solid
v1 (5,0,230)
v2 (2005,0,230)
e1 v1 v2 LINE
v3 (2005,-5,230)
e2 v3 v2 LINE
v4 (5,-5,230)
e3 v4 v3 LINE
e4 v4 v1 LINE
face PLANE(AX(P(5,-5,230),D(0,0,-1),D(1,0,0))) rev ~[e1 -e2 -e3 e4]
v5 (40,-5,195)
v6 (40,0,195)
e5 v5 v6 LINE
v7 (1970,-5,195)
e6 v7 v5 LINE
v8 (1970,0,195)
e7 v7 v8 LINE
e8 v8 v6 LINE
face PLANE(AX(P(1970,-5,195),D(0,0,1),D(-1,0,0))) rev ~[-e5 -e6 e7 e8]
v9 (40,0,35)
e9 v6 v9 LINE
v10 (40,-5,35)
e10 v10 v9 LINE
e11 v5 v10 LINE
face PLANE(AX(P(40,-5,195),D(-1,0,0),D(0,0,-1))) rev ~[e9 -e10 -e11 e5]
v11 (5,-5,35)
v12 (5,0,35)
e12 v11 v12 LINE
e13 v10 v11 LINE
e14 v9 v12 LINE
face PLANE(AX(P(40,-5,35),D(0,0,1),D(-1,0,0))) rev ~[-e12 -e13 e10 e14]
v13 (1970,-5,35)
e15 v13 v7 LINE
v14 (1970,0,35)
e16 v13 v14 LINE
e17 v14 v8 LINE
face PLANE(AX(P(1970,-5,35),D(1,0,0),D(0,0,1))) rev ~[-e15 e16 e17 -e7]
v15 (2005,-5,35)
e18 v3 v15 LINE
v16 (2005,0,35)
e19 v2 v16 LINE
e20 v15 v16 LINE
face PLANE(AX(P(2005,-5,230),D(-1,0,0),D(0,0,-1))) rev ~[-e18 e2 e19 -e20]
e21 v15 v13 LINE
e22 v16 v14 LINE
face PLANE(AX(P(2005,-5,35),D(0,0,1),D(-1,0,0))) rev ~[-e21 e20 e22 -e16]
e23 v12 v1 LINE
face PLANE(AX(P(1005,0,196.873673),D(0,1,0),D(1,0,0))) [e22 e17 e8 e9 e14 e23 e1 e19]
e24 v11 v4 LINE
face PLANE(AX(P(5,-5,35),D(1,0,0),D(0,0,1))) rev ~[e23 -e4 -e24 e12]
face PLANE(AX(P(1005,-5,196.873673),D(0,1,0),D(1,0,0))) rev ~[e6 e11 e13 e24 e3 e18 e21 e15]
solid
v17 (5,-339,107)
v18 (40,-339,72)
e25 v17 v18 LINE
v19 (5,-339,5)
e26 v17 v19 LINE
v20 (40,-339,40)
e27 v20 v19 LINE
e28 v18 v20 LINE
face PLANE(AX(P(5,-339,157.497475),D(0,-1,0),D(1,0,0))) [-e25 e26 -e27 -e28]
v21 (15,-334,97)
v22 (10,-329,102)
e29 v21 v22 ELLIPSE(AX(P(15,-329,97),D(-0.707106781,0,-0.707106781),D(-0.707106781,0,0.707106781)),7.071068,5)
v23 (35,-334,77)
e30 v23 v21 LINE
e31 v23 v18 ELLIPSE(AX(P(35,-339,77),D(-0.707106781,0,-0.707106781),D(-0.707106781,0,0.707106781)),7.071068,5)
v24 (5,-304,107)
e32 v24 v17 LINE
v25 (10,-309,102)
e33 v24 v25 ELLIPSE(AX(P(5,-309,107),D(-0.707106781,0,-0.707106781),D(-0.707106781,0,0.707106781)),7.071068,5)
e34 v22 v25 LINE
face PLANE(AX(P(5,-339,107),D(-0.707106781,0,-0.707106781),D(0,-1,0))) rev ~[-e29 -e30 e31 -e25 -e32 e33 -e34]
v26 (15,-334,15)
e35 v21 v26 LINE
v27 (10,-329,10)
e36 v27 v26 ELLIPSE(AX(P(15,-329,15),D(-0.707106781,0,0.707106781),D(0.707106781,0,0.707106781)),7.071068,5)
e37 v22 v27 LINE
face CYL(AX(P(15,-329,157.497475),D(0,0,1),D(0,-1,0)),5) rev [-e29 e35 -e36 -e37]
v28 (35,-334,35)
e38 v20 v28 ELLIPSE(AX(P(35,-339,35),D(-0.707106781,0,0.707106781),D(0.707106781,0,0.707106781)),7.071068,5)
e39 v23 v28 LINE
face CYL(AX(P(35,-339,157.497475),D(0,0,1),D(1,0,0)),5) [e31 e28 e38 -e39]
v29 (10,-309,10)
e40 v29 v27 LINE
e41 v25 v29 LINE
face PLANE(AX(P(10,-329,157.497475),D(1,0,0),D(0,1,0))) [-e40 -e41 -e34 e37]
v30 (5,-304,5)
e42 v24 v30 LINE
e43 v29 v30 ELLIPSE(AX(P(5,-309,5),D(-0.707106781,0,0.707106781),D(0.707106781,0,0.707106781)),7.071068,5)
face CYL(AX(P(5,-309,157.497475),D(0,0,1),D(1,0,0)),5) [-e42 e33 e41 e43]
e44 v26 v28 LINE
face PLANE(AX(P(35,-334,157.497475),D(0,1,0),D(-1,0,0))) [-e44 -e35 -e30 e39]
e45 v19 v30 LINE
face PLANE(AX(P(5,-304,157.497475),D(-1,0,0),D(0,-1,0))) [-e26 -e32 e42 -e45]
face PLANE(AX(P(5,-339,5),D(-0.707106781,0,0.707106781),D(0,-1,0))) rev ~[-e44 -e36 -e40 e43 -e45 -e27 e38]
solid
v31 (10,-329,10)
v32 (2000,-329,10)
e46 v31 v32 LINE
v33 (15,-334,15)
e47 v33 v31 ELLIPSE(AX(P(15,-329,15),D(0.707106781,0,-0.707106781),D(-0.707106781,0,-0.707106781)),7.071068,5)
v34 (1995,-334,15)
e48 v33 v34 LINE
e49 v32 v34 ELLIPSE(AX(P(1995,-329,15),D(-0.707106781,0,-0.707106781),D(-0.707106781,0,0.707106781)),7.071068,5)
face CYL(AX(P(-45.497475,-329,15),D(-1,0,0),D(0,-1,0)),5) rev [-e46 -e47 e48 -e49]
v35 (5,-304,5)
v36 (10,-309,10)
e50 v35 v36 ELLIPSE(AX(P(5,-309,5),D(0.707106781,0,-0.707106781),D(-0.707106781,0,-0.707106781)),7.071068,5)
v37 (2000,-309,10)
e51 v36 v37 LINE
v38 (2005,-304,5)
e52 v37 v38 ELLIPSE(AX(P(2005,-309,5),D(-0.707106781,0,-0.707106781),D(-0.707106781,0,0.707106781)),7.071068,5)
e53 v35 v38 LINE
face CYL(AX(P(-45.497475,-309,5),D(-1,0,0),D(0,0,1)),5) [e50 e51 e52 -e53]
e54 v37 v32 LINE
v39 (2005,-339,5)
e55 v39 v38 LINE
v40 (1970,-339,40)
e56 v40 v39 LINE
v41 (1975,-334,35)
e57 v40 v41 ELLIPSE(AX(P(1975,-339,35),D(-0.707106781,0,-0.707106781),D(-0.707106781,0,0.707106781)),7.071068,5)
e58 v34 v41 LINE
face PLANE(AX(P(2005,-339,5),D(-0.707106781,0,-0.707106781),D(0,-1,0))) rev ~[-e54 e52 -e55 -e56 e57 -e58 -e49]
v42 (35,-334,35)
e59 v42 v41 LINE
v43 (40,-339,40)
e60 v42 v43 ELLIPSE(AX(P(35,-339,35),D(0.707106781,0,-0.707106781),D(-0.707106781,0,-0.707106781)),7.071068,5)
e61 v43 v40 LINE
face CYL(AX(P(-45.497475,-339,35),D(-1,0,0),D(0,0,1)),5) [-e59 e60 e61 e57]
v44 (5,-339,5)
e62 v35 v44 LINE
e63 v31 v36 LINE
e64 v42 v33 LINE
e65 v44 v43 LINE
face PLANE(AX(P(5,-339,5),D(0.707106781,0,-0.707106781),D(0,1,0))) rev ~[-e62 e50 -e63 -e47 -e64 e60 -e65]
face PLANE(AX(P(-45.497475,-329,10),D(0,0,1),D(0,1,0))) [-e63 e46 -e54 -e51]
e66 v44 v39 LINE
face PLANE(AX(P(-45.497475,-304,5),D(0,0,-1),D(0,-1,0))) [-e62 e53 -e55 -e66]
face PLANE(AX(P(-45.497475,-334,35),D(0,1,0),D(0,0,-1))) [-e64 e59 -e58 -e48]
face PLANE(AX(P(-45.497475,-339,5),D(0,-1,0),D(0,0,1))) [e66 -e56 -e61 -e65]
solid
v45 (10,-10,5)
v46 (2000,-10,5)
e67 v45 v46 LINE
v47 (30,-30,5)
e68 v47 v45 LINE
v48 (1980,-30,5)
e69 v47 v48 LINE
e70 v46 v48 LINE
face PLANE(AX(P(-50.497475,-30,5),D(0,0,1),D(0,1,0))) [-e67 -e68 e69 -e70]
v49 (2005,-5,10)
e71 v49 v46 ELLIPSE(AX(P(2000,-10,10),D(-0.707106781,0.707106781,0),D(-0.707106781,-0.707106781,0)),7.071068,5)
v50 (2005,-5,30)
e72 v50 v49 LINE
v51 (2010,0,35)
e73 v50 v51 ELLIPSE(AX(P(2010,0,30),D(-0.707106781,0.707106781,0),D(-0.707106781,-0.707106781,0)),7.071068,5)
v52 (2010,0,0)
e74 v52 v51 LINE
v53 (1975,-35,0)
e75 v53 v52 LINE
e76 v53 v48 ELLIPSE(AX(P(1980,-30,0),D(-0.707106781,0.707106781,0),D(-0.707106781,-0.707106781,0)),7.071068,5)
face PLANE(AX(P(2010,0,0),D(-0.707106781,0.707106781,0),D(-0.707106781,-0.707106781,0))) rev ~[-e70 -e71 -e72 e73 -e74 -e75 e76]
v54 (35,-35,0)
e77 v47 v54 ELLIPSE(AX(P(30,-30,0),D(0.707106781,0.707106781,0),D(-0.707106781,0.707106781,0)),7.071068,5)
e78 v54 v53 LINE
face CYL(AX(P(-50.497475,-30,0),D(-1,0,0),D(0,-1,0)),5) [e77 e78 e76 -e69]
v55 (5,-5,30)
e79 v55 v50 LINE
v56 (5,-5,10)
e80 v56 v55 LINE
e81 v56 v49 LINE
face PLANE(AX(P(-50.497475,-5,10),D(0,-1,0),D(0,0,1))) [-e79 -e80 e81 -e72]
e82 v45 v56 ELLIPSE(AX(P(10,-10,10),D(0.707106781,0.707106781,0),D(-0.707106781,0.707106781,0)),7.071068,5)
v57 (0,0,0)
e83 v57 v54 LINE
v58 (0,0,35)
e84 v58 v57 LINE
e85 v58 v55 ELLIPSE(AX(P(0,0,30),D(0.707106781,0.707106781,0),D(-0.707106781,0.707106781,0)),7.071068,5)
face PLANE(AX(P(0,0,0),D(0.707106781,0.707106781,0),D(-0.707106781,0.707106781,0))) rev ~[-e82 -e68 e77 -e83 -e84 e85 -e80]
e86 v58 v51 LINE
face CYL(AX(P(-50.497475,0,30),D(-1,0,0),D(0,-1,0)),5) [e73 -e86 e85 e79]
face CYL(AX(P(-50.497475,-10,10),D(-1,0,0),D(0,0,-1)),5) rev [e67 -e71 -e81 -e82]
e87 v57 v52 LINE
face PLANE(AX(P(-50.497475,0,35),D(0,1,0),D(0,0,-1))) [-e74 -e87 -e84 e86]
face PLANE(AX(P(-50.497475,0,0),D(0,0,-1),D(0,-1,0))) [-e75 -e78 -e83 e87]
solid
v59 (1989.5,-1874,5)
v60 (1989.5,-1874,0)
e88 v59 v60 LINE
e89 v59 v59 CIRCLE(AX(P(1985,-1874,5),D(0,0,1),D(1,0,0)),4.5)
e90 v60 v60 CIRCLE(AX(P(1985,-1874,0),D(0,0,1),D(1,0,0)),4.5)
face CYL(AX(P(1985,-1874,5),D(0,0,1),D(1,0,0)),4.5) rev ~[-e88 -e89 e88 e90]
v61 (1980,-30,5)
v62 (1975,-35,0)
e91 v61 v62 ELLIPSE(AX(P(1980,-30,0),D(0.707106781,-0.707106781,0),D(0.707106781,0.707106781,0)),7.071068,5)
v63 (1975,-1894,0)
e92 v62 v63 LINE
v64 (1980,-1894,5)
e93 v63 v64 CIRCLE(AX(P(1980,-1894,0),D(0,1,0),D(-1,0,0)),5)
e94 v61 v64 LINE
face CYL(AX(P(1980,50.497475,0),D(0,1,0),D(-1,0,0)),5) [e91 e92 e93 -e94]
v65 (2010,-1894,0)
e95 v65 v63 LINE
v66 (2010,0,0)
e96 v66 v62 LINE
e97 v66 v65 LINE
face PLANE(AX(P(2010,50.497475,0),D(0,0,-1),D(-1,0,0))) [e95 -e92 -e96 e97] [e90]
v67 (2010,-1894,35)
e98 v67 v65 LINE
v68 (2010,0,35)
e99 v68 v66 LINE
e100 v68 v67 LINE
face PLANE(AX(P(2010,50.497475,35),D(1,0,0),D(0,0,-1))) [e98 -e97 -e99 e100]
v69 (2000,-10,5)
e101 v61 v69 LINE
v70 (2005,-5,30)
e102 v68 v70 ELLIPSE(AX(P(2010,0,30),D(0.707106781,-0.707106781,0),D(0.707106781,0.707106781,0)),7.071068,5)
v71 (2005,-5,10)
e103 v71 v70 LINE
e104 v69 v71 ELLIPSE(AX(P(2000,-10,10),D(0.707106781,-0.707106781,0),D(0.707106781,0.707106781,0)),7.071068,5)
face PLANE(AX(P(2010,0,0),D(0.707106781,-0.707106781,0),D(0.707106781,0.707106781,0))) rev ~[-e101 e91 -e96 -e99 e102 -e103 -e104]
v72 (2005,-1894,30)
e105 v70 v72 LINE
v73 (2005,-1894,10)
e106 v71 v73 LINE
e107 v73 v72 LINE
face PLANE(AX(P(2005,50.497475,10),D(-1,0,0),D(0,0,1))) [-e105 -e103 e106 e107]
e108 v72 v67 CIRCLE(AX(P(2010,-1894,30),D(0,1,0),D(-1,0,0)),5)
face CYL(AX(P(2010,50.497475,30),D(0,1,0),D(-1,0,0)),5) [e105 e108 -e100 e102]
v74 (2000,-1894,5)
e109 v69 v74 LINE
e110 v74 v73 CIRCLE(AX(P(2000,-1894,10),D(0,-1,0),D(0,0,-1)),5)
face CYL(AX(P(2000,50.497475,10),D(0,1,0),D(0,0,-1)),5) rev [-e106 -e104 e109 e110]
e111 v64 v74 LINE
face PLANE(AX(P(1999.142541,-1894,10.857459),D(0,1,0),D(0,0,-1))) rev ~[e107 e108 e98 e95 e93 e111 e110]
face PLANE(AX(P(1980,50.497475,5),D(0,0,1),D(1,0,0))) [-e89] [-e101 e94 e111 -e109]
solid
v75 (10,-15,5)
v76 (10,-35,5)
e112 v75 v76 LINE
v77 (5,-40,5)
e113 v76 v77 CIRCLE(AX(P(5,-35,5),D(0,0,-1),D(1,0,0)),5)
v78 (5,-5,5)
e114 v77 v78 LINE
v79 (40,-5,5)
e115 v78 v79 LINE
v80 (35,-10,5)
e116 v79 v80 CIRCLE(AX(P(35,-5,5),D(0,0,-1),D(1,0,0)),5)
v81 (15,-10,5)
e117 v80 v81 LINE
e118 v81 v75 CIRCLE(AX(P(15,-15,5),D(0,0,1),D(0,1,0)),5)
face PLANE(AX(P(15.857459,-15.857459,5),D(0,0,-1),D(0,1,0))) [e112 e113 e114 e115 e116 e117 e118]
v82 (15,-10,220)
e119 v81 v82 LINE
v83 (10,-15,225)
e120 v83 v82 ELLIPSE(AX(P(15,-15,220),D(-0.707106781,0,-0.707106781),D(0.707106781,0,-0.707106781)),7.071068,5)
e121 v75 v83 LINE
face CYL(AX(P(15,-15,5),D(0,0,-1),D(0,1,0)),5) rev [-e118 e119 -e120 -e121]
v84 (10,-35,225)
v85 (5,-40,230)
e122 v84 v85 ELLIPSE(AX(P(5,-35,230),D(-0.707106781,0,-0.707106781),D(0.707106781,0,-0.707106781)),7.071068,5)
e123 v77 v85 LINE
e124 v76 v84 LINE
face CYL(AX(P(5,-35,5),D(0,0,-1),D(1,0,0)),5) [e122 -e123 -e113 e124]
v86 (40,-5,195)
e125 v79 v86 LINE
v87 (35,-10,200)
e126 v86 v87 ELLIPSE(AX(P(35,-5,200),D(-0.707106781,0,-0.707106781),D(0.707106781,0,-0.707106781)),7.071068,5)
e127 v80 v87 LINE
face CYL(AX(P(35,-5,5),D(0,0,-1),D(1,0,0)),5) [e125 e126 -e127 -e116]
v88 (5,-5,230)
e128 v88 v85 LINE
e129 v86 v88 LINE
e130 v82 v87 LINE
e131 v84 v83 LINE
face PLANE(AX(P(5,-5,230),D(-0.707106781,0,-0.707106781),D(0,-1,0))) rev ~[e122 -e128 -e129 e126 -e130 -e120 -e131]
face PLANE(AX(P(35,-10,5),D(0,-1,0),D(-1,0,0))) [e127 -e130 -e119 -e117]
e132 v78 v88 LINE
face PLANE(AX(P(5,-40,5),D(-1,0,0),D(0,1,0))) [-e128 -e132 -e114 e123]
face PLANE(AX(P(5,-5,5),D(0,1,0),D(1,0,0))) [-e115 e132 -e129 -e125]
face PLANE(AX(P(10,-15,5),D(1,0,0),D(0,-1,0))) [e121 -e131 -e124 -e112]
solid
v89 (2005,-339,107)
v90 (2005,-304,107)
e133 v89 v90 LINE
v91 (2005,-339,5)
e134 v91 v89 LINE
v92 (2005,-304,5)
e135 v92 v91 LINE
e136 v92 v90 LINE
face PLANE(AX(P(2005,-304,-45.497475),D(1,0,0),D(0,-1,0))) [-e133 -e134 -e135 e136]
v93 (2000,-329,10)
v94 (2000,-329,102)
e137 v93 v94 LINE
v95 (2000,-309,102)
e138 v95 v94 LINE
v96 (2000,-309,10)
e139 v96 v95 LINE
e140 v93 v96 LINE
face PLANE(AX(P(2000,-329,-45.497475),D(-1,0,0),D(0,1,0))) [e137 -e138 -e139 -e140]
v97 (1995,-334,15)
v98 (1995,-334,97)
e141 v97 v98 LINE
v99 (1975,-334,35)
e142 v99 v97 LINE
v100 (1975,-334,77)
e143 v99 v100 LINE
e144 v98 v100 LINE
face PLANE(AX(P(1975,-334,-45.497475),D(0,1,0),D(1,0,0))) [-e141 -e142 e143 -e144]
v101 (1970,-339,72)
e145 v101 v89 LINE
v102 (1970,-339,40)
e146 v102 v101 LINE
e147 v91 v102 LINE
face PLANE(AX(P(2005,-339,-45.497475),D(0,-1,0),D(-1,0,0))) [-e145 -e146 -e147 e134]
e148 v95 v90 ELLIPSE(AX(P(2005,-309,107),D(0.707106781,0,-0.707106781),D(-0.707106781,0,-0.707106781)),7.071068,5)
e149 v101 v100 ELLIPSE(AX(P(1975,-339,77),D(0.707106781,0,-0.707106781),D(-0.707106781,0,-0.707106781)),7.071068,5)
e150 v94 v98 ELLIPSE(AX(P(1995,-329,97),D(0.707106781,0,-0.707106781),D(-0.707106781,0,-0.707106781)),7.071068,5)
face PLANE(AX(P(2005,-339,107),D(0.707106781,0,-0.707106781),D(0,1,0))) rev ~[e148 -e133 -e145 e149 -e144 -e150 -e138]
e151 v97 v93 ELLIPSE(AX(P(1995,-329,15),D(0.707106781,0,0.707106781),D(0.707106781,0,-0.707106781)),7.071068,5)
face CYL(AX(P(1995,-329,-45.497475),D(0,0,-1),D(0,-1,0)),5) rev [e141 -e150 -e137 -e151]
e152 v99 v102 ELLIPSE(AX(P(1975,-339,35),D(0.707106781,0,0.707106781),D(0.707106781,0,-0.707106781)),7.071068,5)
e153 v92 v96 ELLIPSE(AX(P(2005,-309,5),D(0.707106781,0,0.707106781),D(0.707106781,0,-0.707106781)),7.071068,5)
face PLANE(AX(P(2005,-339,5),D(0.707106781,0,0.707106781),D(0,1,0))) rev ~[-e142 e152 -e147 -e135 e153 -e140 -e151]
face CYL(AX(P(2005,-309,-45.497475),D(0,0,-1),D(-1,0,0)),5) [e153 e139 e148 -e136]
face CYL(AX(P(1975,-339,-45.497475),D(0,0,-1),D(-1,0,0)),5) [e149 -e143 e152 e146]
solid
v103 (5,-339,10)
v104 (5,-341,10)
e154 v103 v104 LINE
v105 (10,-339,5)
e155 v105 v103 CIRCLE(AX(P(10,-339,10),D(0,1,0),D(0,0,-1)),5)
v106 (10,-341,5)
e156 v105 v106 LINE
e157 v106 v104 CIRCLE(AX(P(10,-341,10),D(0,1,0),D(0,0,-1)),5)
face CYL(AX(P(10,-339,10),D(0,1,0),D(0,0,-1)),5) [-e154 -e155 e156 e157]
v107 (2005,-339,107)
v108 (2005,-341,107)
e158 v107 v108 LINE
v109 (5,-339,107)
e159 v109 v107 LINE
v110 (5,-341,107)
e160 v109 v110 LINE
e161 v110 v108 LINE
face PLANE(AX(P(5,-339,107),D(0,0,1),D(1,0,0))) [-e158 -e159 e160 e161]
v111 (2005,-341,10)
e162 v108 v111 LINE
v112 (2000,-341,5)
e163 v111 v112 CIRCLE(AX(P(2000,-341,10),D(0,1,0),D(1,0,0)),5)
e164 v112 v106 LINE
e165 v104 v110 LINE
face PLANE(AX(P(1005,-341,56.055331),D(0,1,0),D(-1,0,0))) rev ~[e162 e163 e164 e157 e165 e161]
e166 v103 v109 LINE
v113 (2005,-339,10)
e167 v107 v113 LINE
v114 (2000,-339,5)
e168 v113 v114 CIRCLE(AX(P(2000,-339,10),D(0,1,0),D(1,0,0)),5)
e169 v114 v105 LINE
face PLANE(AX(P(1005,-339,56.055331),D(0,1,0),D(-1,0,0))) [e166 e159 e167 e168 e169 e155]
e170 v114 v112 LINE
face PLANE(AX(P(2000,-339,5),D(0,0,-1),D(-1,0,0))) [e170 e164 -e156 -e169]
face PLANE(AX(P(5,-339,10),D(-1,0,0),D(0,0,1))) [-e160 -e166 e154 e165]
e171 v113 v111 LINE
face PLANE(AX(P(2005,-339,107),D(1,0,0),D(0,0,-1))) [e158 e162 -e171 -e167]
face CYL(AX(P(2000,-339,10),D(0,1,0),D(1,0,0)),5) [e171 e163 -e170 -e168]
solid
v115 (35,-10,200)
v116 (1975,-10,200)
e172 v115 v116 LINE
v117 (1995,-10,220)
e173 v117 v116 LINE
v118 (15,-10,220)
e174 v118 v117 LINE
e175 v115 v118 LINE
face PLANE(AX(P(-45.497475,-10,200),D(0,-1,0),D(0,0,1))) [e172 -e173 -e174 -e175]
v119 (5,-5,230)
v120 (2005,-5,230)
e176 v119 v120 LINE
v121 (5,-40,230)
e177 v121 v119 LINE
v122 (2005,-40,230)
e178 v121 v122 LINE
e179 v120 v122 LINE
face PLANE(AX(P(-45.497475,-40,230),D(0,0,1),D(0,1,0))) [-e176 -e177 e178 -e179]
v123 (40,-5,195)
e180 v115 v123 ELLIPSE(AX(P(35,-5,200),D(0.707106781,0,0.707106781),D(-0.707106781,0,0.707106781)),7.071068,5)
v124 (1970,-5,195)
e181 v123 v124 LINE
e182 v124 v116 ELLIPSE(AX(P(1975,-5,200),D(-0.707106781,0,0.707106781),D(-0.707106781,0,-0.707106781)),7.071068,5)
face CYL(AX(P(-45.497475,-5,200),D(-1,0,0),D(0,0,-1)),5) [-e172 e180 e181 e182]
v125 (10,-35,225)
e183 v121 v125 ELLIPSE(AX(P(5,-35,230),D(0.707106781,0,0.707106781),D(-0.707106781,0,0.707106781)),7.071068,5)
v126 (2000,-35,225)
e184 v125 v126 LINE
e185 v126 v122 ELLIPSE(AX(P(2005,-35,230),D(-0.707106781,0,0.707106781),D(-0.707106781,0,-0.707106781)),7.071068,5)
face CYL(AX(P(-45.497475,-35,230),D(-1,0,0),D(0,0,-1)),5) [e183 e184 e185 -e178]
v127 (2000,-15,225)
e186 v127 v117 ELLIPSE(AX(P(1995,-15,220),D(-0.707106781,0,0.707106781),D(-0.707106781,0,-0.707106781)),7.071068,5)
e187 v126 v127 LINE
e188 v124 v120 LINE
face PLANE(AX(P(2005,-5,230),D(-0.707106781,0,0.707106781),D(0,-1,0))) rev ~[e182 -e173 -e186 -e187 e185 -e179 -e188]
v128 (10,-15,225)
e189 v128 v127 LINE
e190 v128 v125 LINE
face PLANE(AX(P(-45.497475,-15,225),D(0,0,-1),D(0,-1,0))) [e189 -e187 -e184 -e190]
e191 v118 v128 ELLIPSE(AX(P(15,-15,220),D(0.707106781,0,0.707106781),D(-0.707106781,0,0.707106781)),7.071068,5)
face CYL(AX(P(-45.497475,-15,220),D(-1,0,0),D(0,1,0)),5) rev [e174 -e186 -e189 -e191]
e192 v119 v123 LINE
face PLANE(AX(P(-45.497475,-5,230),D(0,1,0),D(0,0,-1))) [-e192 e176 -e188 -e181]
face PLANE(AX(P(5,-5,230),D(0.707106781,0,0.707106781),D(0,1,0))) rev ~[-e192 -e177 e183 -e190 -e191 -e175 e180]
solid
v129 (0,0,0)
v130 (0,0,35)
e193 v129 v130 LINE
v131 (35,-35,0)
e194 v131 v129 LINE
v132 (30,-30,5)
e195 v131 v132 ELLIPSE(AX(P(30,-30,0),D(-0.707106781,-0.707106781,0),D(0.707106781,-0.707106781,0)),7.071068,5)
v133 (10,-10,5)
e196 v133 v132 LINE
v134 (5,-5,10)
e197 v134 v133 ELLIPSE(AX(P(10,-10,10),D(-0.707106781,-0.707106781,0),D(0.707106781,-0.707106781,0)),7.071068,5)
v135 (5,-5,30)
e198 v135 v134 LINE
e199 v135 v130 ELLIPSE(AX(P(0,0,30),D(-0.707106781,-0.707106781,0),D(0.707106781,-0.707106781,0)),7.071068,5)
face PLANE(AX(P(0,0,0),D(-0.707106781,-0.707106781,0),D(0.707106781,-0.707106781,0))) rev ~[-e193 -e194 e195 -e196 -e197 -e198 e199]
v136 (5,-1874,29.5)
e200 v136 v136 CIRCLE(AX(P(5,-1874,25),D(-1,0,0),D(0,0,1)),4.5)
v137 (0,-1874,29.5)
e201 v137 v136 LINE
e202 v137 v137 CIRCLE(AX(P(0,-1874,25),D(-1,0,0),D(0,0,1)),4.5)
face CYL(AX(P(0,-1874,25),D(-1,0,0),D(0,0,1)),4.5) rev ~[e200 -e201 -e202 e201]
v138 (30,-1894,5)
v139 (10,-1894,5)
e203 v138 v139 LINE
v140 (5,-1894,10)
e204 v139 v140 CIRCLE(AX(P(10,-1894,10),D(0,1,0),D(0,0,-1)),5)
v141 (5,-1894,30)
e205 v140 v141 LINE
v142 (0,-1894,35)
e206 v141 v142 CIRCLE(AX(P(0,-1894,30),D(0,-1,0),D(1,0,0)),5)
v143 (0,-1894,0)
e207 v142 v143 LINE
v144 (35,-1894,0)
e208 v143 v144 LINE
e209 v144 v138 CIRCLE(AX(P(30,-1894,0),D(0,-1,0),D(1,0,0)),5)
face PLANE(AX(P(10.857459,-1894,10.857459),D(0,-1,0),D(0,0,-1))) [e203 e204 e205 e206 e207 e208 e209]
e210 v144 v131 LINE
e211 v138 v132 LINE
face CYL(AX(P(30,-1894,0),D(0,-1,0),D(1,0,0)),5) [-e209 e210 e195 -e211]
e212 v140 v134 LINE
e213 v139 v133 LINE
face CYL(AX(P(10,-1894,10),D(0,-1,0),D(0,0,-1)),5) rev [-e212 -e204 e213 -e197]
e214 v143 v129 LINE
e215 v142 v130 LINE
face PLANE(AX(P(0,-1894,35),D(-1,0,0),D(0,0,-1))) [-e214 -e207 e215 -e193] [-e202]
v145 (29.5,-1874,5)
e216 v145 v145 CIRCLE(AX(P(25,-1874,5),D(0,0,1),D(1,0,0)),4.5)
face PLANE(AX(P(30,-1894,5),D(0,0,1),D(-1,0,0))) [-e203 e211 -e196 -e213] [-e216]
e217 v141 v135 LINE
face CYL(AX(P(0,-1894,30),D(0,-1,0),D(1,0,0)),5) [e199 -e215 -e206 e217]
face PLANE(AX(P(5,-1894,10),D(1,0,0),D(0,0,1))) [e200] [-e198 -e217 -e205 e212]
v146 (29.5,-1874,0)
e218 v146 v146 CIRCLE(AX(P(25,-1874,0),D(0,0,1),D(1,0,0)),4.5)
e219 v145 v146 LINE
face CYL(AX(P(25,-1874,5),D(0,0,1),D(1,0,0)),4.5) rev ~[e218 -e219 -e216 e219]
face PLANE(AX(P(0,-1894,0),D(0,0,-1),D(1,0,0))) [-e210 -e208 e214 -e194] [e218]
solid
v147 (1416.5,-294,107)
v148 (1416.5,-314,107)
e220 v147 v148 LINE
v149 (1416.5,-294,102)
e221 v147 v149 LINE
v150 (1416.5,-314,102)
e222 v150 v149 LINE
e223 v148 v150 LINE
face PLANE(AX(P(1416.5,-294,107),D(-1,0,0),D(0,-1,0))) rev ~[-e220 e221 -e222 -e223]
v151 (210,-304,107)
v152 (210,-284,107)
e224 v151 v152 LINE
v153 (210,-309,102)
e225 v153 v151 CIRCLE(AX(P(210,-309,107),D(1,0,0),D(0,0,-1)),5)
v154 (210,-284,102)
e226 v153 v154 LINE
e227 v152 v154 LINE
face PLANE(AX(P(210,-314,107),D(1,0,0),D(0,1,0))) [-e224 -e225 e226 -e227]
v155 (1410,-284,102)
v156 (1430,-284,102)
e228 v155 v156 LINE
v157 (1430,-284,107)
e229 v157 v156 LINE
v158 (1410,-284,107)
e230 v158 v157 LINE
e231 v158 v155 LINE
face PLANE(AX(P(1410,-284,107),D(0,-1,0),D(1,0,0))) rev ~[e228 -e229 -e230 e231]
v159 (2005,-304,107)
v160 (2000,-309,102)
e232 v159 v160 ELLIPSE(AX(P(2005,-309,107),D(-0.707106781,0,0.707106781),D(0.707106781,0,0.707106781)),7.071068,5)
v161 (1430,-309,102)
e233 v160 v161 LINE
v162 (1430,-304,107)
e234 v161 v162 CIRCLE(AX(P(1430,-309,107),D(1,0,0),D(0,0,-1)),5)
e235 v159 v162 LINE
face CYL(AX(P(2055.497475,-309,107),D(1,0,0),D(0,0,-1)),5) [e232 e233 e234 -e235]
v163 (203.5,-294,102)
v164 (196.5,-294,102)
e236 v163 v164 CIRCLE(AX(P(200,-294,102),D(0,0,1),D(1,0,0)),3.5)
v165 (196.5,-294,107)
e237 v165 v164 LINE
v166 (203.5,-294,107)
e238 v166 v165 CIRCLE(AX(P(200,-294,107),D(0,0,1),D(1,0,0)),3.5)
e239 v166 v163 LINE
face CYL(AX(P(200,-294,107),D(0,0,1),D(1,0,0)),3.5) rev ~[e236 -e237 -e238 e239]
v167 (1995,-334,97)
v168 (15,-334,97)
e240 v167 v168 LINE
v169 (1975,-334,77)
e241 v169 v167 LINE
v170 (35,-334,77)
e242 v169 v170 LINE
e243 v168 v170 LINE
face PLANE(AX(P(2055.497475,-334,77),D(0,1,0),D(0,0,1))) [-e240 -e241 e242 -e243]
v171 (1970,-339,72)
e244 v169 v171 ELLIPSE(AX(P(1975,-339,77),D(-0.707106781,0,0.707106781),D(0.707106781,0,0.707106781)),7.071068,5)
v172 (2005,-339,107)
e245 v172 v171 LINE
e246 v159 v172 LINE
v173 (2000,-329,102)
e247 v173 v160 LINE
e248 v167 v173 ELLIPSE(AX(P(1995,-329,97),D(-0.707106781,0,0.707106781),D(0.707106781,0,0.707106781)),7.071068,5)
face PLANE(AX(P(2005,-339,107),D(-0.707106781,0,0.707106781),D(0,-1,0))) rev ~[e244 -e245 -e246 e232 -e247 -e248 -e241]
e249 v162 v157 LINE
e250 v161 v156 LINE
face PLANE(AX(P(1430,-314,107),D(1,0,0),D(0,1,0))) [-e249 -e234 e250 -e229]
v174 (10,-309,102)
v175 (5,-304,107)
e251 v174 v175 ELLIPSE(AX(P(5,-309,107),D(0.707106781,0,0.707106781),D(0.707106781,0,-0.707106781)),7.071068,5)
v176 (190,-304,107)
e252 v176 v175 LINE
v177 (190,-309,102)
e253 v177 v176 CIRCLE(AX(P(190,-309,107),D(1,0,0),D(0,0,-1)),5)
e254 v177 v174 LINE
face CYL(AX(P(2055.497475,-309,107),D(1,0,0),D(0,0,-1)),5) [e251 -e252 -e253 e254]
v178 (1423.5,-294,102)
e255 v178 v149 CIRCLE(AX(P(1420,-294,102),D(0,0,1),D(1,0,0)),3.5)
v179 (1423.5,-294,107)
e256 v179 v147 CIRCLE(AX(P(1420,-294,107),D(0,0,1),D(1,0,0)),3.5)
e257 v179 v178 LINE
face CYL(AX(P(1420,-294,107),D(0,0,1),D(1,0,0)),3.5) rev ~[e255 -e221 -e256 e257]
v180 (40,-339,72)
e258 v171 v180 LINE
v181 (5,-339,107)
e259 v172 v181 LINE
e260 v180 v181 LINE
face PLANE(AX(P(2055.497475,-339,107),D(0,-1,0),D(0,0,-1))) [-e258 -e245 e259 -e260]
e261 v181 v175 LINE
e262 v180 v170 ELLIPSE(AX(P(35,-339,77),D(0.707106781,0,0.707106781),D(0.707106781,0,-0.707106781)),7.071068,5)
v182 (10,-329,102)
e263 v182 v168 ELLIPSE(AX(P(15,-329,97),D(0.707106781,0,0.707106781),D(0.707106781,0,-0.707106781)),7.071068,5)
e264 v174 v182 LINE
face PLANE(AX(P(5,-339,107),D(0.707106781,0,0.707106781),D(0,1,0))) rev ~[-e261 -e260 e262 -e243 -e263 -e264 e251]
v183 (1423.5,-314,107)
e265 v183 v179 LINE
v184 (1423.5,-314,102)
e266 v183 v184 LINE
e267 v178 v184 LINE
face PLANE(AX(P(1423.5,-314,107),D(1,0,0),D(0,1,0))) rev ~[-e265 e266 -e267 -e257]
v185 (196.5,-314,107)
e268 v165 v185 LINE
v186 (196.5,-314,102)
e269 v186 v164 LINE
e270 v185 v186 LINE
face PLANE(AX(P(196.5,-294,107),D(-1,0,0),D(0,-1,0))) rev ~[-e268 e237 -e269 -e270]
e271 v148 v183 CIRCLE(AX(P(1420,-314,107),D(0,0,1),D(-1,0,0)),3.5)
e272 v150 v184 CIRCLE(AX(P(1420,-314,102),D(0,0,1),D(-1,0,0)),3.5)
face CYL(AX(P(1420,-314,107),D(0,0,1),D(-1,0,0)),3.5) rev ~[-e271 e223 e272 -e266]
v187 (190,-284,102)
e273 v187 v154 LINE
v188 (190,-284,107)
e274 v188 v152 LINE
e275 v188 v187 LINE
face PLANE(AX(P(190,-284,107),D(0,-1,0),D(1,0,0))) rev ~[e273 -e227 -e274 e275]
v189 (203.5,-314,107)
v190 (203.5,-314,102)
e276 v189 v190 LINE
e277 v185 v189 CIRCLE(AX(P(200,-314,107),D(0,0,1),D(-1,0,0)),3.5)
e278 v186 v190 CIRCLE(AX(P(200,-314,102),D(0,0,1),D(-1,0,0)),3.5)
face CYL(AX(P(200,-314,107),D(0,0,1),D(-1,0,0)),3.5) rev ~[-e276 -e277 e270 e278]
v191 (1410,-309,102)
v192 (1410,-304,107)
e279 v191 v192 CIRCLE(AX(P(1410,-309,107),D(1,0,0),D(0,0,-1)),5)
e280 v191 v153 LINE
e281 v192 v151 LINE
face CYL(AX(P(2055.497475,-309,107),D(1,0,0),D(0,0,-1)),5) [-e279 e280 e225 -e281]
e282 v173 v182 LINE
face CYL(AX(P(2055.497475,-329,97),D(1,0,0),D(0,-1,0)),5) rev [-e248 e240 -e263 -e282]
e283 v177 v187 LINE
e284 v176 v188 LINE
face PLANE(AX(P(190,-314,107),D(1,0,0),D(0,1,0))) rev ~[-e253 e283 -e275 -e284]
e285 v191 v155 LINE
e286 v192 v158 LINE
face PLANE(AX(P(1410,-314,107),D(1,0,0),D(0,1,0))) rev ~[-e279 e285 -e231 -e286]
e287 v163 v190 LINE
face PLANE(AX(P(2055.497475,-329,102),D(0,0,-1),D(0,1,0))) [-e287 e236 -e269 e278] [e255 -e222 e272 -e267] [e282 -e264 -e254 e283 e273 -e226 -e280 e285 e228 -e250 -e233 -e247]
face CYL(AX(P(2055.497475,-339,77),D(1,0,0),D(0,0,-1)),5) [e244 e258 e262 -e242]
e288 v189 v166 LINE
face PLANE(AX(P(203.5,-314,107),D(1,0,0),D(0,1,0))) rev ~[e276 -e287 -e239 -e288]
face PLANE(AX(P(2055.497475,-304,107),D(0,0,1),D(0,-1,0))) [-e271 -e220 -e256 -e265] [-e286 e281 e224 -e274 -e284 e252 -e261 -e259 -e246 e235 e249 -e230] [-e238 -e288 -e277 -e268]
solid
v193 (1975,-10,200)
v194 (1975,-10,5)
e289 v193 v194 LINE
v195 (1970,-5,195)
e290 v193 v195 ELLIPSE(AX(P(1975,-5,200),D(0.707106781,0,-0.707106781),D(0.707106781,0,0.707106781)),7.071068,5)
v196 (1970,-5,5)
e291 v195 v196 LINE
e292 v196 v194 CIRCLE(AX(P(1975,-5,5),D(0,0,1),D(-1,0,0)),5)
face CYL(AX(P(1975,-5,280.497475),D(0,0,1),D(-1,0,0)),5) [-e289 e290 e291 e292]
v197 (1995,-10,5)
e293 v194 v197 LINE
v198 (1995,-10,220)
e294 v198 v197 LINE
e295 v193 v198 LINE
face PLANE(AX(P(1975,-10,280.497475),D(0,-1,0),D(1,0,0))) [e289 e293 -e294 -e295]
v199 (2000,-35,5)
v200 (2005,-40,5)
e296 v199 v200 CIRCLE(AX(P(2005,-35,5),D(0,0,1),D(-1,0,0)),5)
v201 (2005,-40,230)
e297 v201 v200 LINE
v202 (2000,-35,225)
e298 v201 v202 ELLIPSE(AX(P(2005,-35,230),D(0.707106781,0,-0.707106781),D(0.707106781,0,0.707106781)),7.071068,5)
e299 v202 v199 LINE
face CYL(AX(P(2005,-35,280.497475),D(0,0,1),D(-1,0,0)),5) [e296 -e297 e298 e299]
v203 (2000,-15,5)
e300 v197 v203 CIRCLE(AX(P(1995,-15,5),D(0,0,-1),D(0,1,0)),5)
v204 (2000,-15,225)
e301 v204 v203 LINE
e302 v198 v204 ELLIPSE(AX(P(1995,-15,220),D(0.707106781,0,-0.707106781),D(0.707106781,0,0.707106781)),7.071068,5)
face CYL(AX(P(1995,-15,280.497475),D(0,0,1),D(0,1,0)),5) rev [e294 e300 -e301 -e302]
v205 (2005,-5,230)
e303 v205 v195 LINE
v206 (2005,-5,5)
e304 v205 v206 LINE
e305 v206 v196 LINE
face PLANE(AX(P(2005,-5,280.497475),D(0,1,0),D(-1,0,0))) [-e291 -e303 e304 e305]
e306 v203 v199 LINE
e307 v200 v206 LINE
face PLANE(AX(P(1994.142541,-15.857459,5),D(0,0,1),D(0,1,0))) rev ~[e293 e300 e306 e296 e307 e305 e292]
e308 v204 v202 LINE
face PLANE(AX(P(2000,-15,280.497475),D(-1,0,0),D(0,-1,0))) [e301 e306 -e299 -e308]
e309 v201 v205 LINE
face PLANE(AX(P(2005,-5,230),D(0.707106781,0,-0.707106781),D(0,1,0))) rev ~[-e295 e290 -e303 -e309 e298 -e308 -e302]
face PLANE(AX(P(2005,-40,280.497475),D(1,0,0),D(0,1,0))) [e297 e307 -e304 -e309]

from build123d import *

# Parameters (mm, degrees)
MEMBER_1_DEPTH        = 1944.497474683
MEMBER_1_2_DEPTH      = 2060.497474683
MEMBER_1_2_DEPTH_BACK = 50.497474683
MEMBER_1_3_DEPTH      = 1944.497474683
MEMBER_2_DEPTH        = 275.497474683
MEMBER_2_2_DEPTH      = 2100.994949366
MEMBER_2_3_DEPTH      = 275.497474683
MEMBER_3_DEPTH        = 152.497474683
MEMBER_3_DEPTH_BACK   = 50.497474683
MEMBER_3_2_DEPTH      = 2100.994949366
MEMBER_3_3_DEPTH      = 202.994949366
MEMBER_3_4_DEPTH      = 2100.994949366
SKETCH_8_R            = 4.5
CUT_EXTRUDE_1_DEPTH   = 10
SKETCH_9_R            = 4.5
CUT_EXTRUDE_2_DEPTH   = 697
EXTRUDE_1_DEPTH       = 5
EXTRUDE_2_DEPTH       = 2
SKETCH_13_W           = 20
SKETCH_13_H           = 30
EXTRUDE_3_DEPTH       = 5
CUT_EXTRUDE_3_DEPTH   = 10


with BuildPart() as part:
    # Sketch1 on segment 1 (carried to segment 1) → Member 1 (new body)
    with BuildSketch(Plane.ZX.offset(-1894)):
        with BuildLine():
            Line((0, 0), (0, 35))
            ThreePointArc((0, 35), (3.535533906, 33.535533906), (5, 30))
            Line((5, 30), (5, 10))
            ThreePointArc((5, 10), (6.464466094, 6.464466094), (10, 5))
            Line((10, 5), (30, 5))
            ThreePointArc((30, 5), (33.535533906, 3.535533906), (35, 0))
            Line((35, 0), (0, 0))
        make_face()
    extrude(amount=MEMBER_1_DEPTH)

    # Member 1 mitre 1
    split(bisect_by=Plane(origin=(0, 0, 0), x_dir=(0.707106781, -0.707106781, 0), z_dir=(-0.707106781, -0.707106781, 0)), keep=Keep.TOP)


with BuildPart() as body_2:
    # Sketch1 → Member 1 2 (new, two sides: drawn at the far end of the back side and taken through both)
    with BuildSketch(Plane(origin=(0, 0, 0), x_dir=(0, 0, 1), z_dir=(1, 0, 0)).offset(-MEMBER_1_2_DEPTH_BACK)):
        with BuildLine():
            Line((0, 0), (0, 35))
            ThreePointArc((0, 35), (3.535533906, 33.535533906), (5, 30))
            Line((5, 30), (5, 10))
            ThreePointArc((5, 10), (6.464466094, 6.464466094), (10, 5))
            Line((10, 5), (30, 5))
            ThreePointArc((30, 5), (33.535533906, 3.535533906), (35, 0))
            Line((35, 0), (0, 0))
        make_face()
    extrude(amount=MEMBER_1_2_DEPTH + MEMBER_1_2_DEPTH_BACK)

    # Member 1 2 mitre 1
    split(bisect_by=Plane(origin=(0, 0, 0), x_dir=(-0.707106781, 0.707106781, 0), z_dir=(0.707106781, 0.707106781, 0)), keep=Keep.TOP)

    # Member 1 2 mitre 2
    split(bisect_by=Plane(origin=(2010, 0, 0), x_dir=(-0.707106781, -0.707106781, 0), z_dir=(-0.707106781, 0.707106781, 0)), keep=Keep.TOP)


with BuildPart() as body_3:
    # Sketch1 on segment 3 (carried to segment 3) → Member 1 3 (new body)
    with BuildSketch(Plane(origin=(2010, 50.497474683, 0), x_dir=(0, 0, 1), z_dir=(0, -1, 0))):
        with BuildLine():
            Line((0, 0), (0, 35))
            ThreePointArc((0, 35), (3.535533906, 33.535533906), (5, 30))
            Line((5, 30), (5, 10))
            ThreePointArc((5, 10), (6.464466094, 6.464466094), (10, 5))
            Line((10, 5), (30, 5))
            ThreePointArc((30, 5), (33.535533906, 3.535533906), (35, 0))
            Line((35, 0), (0, 0))
        make_face()
    extrude(amount=MEMBER_1_3_DEPTH)

    # Member 1 3 mitre 1
    split(bisect_by=Plane(origin=(2010, 0, 0), x_dir=(0.707106781, 0.707106781, 0), z_dir=(0.707106781, -0.707106781, 0)), keep=Keep.TOP)


with BuildPart() as body_4:
    # Sketch11 → Member 2 (new body)
    with BuildSketch(Plane(origin=(5, -5, 5), x_dir=(0, -1, 0), z_dir=(0, 0, 1))):
        with BuildLine():
            Line((0, 0), (0, 35))
            ThreePointArc((0, 35), (3.535533906, 33.535533906), (5, 30))
            Line((5, 30), (5, 10))
            ThreePointArc((5, 10), (6.464466094, 6.464466094), (10, 5))
            Line((10, 5), (30, 5))
            ThreePointArc((30, 5), (33.535533906, 3.535533906), (35, 0))
            Line((35, 0), (0, 0))
        make_face()
    extrude(amount=MEMBER_2_DEPTH)

    # Member 2 mitre 1
    split(bisect_by=Plane(origin=(5, -5, 230), x_dir=(0, -1, 0), z_dir=(-0.707106781, 0, -0.707106781)), keep=Keep.TOP)


with BuildPart() as body_5:
    # Sketch11 on segment 2 (carried to segment 2) → Member 2 2 (new body)
    with BuildSketch(Plane(origin=(-45.497474683, -5, 230), x_dir=(0, -1, 0), z_dir=(1, 0, 0))):
        with BuildLine():
            Line((0, 0), (0, 35))
            ThreePointArc((0, 35), (3.535533906, 33.535533906), (5, 30))
            Line((5, 30), (5, 10))
            ThreePointArc((5, 10), (6.464466094, 6.464466094), (10, 5))
            Line((10, 5), (30, 5))
            ThreePointArc((30, 5), (33.535533906, 3.535533906), (35, 0))
            Line((35, 0), (0, 0))
        make_face()
    extrude(amount=MEMBER_2_2_DEPTH)

    # Member 2 2 mitre 1
    split(bisect_by=Plane(origin=(2005, -5, 230), x_dir=(0, -1, 0), z_dir=(-0.707106781, 0, 0.707106781)), keep=Keep.TOP)

    # Member 2 2 mitre 2
    split(bisect_by=Plane(origin=(5, -5, 230), x_dir=(0, 1, 0), z_dir=(0.707106781, 0, 0.707106781)), keep=Keep.TOP)


with BuildPart() as body_6:
    # Sketch11 on segment 3 (carried to segment 3) → Member 2 3 (new body)
    with BuildSketch(Plane(origin=(2005, -5, 280.497474683), x_dir=(0, -1, 0), z_dir=(0, 0, -1))):
        with BuildLine():
            Line((0, 0), (0, 35))
            ThreePointArc((0, 35), (3.535533906, 33.535533906), (5, 30))
            Line((5, 30), (5, 10))
            ThreePointArc((5, 10), (6.464466094, 6.464466094), (10, 5))
            Line((10, 5), (30, 5))
            ThreePointArc((30, 5), (33.535533906, 3.535533906), (35, 0))
            Line((35, 0), (0, 0))
        make_face()
    extrude(amount=MEMBER_2_3_DEPTH)

    # Member 2 3 mitre 1
    split(bisect_by=Plane(origin=(2005, -5, 230), x_dir=(0, 1, 0), z_dir=(0.707106781, 0, -0.707106781)), keep=Keep.TOP)


with BuildPart() as body_7:
    # Sketch12 → Member 3 (new, two sides: drawn at the far end of the back side and taken through both)
    with BuildSketch(Plane(origin=(2005, -339, 5), x_dir=(0, 1, 0), z_dir=(0, 0, 1)).offset(-MEMBER_3_DEPTH_BACK)):
        with BuildLine():
            Line((0, 0), (0, 35))
            ThreePointArc((0, 35), (3.535533906, 33.535533906), (5, 30))
            Line((5, 30), (5, 10))
            ThreePointArc((5, 10), (6.464466094, 6.464466094), (10, 5))
            Line((10, 5), (30, 5))
            ThreePointArc((30, 5), (33.535533906, 3.535533906), (35, 0))
            Line((35, 0), (0, 0))
        make_face()
    extrude(amount=MEMBER_3_DEPTH + MEMBER_3_DEPTH_BACK)

    # Member 3 mitre 1
    split(bisect_by=Plane(origin=(2005, -339, 5), x_dir=(0, 1, 0), z_dir=(0.707106781, 0, 0.707106781)), keep=Keep.TOP)

    # Member 3 mitre 2
    split(bisect_by=Plane(origin=(2005, -339, 107), x_dir=(0, 1, 0), z_dir=(0.707106781, 0, -0.707106781)), keep=Keep.TOP)


with BuildPart() as body_8:
    # Sketch12 on segment 2 (carried to segment 2) → Member 3 2 (new body)
    with BuildSketch(Plane(origin=(2055.497474683, -339, 107), x_dir=(0, 1, 0), z_dir=(-1, 0, 0))):
        with BuildLine():
            Line((0, 0), (0, 35))
            ThreePointArc((0, 35), (3.535533906, 33.535533906), (5, 30))
            Line((5, 30), (5, 10))
            ThreePointArc((5, 10), (6.464466094, 6.464466094), (10, 5))
            Line((10, 5), (30, 5))
            ThreePointArc((30, 5), (33.535533906, 3.535533906), (35, 0))
            Line((35, 0), (0, 0))
        make_face()
    extrude(amount=MEMBER_3_2_DEPTH)

    # Member 3 2 mitre 1
    split(bisect_by=Plane(origin=(2005, -339, 107), x_dir=(0, -1, 0), z_dir=(-0.707106781, 0, 0.707106781)), keep=Keep.TOP)

    # Member 3 2 mitre 2
    split(bisect_by=Plane(origin=(5, -339, 107), x_dir=(0, 1, 0), z_dir=(0.707106781, 0, 0.707106781)), keep=Keep.TOP)

    # 草图13 → 凸台-拉伸3 (add)
    with BuildSketch(Plane.XY.offset(107)):
        with Locations((200, -299)):
            Rectangle(SKETCH_13_W, SKETCH_13_H)
        with Locations((1420, -299)):
            Rectangle(SKETCH_13_W, SKETCH_13_H)
    extrude(amount=-EXTRUDE_3_DEPTH)

    # 草图12 → 切除-拉伸3 (cut)
    with BuildSketch(Plane.XY.offset(107)):
        with BuildLine():
            Line((196.5, -294), (196.5, -314))
            ThreePointArc((196.5, -314), (200, -317.5), (203.5, -314))
            Line((203.5, -314), (203.5, -294))
            ThreePointArc((203.5, -294), (200, -290.5), (196.5, -294))
        make_face()
        with BuildLine():
            Line((1416.5, -294), (1416.5, -314))
            ThreePointArc((1416.5, -314), (1420, -317.5), (1423.5, -314))
            Line((1423.5, -314), (1423.5, -294))
            ThreePointArc((1423.5, -294), (1420, -290.5), (1416.5, -294))
        make_face()
    extrude(amount=-CUT_EXTRUDE_3_DEPTH, mode=Mode.SUBTRACT)


with BuildPart() as body_9:
    # Sketch12 on segment 3 (carried to segment 3) → Member 3 3 (new body)
    with BuildSketch(Plane(origin=(5, -339, 157.497474683), x_dir=(0, 1, 0), z_dir=(0, 0, -1))):
        with BuildLine():
            Line((0, 0), (0, 35))
            ThreePointArc((0, 35), (3.535533906, 33.535533906), (5, 30))
            Line((5, 30), (5, 10))
            ThreePointArc((5, 10), (6.464466094, 6.464466094), (10, 5))
            Line((10, 5), (30, 5))
            ThreePointArc((30, 5), (33.535533906, 3.535533906), (35, 0))
            Line((35, 0), (0, 0))
        make_face()
    extrude(amount=MEMBER_3_3_DEPTH)

    # Member 3 3 mitre 1
    split(bisect_by=Plane(origin=(5, -339, 107), x_dir=(0, -1, 0), z_dir=(-0.707106781, 0, -0.707106781)), keep=Keep.TOP)

    # Member 3 3 mitre 2
    split(bisect_by=Plane(origin=(5, -339, 5), x_dir=(0, -1, 0), z_dir=(-0.707106781, 0, 0.707106781)), keep=Keep.TOP)


with BuildPart() as body_10:
    # Sketch12 on segment 4 (carried to segment 4) → Member 3 4 (new body)
    with BuildSketch(Plane(origin=(-45.497474683, -339, 5), x_dir=(0, 1, 0), z_dir=(1, 0, 0))):
        with BuildLine():
            Line((0, 0), (0, 35))
            ThreePointArc((0, 35), (3.535533906, 33.535533906), (5, 30))
            Line((5, 30), (5, 10))
            ThreePointArc((5, 10), (6.464466094, 6.464466094), (10, 5))
            Line((10, 5), (30, 5))
            ThreePointArc((30, 5), (33.535533906, 3.535533906), (35, 0))
            Line((35, 0), (0, 0))
        make_face()
    extrude(amount=MEMBER_3_4_DEPTH)

    # Member 3 4 mitre 1
    split(bisect_by=Plane(origin=(2005, -339, 5), x_dir=(0, -1, 0), z_dir=(-0.707106781, 0, -0.707106781)), keep=Keep.TOP)

    # Member 3 4 mitre 2
    split(bisect_by=Plane(origin=(5, -339, 5), x_dir=(0, 1, 0), z_dir=(0.707106781, 0, -0.707106781)), keep=Keep.TOP)


with BuildPart() as cut_extrude_1_tool:
    # 草图8 → 切除-拉伸1 (new body)
    with BuildSketch(Plane.XY.offset(5)):
        with Locations((25, -1874)):
            Circle(SKETCH_8_R)
        with Locations((1985, -1874)):
            Circle(SKETCH_8_R)
    extrude(amount=-CUT_EXTRUDE_1_DEPTH)


with BuildPart() as part_1:
    add(part.part)

    # 切除-拉伸1: cut by cut_extrude_1_tool
    add(cut_extrude_1_tool.part, mode=Mode.SUBTRACT)

    # 草图9 → 切除-拉伸2 (cut)
    with BuildSketch(Plane.ZY):
        with Locations((25, -1874)):
            Circle(SKETCH_9_R)
    extrude(amount=-CUT_EXTRUDE_2_DEPTH, mode=Mode.SUBTRACT)


with BuildPart() as body_3_1:
    add(body_3.part)

    # 切除-拉伸1: cut by cut_extrude_1_tool
    add(cut_extrude_1_tool.part, mode=Mode.SUBTRACT)


with BuildPart() as body_11:
    # 草图10 → 凸台-拉伸1 (new body)
    with BuildSketch(Plane(origin=(0, -5, 0), x_dir=(1, 0, 0), z_dir=(0, 1, 0))):
        Polygon((5, -35), (5, -230), (2005, -230), (2005, -35), (1970, -35), (1970, -195), (40, -195), (40, -35), align=None)
    extrude(amount=EXTRUDE_1_DEPTH)


with BuildPart() as body_12:
    # 草图11 → 凸台-拉伸2 (new body)
    with BuildSketch(Plane.XZ.offset(339)):
        with BuildLine():
            Line((5, 107), (2005, 107))
            Line((2005, 107), (2005, 10))
            ThreePointArc((2005, 10), (2003.535533906, 6.464466094), (2000, 5))
            Line((2000, 5), (10, 5))
            ThreePointArc((10, 5), (6.464466094, 6.464466094), (5, 10))
            Line((5, 10), (5, 107))
        make_face()
    extrude(amount=EXTRUDE_2_DEPTH)


solid = Compound([body_2.part, body_4.part, body_5.part, body_6.part, body_7.part, body_8.part, body_9.part, body_10.part, part_1.part, body_3_1.part, body_11.part, body_12.part])
